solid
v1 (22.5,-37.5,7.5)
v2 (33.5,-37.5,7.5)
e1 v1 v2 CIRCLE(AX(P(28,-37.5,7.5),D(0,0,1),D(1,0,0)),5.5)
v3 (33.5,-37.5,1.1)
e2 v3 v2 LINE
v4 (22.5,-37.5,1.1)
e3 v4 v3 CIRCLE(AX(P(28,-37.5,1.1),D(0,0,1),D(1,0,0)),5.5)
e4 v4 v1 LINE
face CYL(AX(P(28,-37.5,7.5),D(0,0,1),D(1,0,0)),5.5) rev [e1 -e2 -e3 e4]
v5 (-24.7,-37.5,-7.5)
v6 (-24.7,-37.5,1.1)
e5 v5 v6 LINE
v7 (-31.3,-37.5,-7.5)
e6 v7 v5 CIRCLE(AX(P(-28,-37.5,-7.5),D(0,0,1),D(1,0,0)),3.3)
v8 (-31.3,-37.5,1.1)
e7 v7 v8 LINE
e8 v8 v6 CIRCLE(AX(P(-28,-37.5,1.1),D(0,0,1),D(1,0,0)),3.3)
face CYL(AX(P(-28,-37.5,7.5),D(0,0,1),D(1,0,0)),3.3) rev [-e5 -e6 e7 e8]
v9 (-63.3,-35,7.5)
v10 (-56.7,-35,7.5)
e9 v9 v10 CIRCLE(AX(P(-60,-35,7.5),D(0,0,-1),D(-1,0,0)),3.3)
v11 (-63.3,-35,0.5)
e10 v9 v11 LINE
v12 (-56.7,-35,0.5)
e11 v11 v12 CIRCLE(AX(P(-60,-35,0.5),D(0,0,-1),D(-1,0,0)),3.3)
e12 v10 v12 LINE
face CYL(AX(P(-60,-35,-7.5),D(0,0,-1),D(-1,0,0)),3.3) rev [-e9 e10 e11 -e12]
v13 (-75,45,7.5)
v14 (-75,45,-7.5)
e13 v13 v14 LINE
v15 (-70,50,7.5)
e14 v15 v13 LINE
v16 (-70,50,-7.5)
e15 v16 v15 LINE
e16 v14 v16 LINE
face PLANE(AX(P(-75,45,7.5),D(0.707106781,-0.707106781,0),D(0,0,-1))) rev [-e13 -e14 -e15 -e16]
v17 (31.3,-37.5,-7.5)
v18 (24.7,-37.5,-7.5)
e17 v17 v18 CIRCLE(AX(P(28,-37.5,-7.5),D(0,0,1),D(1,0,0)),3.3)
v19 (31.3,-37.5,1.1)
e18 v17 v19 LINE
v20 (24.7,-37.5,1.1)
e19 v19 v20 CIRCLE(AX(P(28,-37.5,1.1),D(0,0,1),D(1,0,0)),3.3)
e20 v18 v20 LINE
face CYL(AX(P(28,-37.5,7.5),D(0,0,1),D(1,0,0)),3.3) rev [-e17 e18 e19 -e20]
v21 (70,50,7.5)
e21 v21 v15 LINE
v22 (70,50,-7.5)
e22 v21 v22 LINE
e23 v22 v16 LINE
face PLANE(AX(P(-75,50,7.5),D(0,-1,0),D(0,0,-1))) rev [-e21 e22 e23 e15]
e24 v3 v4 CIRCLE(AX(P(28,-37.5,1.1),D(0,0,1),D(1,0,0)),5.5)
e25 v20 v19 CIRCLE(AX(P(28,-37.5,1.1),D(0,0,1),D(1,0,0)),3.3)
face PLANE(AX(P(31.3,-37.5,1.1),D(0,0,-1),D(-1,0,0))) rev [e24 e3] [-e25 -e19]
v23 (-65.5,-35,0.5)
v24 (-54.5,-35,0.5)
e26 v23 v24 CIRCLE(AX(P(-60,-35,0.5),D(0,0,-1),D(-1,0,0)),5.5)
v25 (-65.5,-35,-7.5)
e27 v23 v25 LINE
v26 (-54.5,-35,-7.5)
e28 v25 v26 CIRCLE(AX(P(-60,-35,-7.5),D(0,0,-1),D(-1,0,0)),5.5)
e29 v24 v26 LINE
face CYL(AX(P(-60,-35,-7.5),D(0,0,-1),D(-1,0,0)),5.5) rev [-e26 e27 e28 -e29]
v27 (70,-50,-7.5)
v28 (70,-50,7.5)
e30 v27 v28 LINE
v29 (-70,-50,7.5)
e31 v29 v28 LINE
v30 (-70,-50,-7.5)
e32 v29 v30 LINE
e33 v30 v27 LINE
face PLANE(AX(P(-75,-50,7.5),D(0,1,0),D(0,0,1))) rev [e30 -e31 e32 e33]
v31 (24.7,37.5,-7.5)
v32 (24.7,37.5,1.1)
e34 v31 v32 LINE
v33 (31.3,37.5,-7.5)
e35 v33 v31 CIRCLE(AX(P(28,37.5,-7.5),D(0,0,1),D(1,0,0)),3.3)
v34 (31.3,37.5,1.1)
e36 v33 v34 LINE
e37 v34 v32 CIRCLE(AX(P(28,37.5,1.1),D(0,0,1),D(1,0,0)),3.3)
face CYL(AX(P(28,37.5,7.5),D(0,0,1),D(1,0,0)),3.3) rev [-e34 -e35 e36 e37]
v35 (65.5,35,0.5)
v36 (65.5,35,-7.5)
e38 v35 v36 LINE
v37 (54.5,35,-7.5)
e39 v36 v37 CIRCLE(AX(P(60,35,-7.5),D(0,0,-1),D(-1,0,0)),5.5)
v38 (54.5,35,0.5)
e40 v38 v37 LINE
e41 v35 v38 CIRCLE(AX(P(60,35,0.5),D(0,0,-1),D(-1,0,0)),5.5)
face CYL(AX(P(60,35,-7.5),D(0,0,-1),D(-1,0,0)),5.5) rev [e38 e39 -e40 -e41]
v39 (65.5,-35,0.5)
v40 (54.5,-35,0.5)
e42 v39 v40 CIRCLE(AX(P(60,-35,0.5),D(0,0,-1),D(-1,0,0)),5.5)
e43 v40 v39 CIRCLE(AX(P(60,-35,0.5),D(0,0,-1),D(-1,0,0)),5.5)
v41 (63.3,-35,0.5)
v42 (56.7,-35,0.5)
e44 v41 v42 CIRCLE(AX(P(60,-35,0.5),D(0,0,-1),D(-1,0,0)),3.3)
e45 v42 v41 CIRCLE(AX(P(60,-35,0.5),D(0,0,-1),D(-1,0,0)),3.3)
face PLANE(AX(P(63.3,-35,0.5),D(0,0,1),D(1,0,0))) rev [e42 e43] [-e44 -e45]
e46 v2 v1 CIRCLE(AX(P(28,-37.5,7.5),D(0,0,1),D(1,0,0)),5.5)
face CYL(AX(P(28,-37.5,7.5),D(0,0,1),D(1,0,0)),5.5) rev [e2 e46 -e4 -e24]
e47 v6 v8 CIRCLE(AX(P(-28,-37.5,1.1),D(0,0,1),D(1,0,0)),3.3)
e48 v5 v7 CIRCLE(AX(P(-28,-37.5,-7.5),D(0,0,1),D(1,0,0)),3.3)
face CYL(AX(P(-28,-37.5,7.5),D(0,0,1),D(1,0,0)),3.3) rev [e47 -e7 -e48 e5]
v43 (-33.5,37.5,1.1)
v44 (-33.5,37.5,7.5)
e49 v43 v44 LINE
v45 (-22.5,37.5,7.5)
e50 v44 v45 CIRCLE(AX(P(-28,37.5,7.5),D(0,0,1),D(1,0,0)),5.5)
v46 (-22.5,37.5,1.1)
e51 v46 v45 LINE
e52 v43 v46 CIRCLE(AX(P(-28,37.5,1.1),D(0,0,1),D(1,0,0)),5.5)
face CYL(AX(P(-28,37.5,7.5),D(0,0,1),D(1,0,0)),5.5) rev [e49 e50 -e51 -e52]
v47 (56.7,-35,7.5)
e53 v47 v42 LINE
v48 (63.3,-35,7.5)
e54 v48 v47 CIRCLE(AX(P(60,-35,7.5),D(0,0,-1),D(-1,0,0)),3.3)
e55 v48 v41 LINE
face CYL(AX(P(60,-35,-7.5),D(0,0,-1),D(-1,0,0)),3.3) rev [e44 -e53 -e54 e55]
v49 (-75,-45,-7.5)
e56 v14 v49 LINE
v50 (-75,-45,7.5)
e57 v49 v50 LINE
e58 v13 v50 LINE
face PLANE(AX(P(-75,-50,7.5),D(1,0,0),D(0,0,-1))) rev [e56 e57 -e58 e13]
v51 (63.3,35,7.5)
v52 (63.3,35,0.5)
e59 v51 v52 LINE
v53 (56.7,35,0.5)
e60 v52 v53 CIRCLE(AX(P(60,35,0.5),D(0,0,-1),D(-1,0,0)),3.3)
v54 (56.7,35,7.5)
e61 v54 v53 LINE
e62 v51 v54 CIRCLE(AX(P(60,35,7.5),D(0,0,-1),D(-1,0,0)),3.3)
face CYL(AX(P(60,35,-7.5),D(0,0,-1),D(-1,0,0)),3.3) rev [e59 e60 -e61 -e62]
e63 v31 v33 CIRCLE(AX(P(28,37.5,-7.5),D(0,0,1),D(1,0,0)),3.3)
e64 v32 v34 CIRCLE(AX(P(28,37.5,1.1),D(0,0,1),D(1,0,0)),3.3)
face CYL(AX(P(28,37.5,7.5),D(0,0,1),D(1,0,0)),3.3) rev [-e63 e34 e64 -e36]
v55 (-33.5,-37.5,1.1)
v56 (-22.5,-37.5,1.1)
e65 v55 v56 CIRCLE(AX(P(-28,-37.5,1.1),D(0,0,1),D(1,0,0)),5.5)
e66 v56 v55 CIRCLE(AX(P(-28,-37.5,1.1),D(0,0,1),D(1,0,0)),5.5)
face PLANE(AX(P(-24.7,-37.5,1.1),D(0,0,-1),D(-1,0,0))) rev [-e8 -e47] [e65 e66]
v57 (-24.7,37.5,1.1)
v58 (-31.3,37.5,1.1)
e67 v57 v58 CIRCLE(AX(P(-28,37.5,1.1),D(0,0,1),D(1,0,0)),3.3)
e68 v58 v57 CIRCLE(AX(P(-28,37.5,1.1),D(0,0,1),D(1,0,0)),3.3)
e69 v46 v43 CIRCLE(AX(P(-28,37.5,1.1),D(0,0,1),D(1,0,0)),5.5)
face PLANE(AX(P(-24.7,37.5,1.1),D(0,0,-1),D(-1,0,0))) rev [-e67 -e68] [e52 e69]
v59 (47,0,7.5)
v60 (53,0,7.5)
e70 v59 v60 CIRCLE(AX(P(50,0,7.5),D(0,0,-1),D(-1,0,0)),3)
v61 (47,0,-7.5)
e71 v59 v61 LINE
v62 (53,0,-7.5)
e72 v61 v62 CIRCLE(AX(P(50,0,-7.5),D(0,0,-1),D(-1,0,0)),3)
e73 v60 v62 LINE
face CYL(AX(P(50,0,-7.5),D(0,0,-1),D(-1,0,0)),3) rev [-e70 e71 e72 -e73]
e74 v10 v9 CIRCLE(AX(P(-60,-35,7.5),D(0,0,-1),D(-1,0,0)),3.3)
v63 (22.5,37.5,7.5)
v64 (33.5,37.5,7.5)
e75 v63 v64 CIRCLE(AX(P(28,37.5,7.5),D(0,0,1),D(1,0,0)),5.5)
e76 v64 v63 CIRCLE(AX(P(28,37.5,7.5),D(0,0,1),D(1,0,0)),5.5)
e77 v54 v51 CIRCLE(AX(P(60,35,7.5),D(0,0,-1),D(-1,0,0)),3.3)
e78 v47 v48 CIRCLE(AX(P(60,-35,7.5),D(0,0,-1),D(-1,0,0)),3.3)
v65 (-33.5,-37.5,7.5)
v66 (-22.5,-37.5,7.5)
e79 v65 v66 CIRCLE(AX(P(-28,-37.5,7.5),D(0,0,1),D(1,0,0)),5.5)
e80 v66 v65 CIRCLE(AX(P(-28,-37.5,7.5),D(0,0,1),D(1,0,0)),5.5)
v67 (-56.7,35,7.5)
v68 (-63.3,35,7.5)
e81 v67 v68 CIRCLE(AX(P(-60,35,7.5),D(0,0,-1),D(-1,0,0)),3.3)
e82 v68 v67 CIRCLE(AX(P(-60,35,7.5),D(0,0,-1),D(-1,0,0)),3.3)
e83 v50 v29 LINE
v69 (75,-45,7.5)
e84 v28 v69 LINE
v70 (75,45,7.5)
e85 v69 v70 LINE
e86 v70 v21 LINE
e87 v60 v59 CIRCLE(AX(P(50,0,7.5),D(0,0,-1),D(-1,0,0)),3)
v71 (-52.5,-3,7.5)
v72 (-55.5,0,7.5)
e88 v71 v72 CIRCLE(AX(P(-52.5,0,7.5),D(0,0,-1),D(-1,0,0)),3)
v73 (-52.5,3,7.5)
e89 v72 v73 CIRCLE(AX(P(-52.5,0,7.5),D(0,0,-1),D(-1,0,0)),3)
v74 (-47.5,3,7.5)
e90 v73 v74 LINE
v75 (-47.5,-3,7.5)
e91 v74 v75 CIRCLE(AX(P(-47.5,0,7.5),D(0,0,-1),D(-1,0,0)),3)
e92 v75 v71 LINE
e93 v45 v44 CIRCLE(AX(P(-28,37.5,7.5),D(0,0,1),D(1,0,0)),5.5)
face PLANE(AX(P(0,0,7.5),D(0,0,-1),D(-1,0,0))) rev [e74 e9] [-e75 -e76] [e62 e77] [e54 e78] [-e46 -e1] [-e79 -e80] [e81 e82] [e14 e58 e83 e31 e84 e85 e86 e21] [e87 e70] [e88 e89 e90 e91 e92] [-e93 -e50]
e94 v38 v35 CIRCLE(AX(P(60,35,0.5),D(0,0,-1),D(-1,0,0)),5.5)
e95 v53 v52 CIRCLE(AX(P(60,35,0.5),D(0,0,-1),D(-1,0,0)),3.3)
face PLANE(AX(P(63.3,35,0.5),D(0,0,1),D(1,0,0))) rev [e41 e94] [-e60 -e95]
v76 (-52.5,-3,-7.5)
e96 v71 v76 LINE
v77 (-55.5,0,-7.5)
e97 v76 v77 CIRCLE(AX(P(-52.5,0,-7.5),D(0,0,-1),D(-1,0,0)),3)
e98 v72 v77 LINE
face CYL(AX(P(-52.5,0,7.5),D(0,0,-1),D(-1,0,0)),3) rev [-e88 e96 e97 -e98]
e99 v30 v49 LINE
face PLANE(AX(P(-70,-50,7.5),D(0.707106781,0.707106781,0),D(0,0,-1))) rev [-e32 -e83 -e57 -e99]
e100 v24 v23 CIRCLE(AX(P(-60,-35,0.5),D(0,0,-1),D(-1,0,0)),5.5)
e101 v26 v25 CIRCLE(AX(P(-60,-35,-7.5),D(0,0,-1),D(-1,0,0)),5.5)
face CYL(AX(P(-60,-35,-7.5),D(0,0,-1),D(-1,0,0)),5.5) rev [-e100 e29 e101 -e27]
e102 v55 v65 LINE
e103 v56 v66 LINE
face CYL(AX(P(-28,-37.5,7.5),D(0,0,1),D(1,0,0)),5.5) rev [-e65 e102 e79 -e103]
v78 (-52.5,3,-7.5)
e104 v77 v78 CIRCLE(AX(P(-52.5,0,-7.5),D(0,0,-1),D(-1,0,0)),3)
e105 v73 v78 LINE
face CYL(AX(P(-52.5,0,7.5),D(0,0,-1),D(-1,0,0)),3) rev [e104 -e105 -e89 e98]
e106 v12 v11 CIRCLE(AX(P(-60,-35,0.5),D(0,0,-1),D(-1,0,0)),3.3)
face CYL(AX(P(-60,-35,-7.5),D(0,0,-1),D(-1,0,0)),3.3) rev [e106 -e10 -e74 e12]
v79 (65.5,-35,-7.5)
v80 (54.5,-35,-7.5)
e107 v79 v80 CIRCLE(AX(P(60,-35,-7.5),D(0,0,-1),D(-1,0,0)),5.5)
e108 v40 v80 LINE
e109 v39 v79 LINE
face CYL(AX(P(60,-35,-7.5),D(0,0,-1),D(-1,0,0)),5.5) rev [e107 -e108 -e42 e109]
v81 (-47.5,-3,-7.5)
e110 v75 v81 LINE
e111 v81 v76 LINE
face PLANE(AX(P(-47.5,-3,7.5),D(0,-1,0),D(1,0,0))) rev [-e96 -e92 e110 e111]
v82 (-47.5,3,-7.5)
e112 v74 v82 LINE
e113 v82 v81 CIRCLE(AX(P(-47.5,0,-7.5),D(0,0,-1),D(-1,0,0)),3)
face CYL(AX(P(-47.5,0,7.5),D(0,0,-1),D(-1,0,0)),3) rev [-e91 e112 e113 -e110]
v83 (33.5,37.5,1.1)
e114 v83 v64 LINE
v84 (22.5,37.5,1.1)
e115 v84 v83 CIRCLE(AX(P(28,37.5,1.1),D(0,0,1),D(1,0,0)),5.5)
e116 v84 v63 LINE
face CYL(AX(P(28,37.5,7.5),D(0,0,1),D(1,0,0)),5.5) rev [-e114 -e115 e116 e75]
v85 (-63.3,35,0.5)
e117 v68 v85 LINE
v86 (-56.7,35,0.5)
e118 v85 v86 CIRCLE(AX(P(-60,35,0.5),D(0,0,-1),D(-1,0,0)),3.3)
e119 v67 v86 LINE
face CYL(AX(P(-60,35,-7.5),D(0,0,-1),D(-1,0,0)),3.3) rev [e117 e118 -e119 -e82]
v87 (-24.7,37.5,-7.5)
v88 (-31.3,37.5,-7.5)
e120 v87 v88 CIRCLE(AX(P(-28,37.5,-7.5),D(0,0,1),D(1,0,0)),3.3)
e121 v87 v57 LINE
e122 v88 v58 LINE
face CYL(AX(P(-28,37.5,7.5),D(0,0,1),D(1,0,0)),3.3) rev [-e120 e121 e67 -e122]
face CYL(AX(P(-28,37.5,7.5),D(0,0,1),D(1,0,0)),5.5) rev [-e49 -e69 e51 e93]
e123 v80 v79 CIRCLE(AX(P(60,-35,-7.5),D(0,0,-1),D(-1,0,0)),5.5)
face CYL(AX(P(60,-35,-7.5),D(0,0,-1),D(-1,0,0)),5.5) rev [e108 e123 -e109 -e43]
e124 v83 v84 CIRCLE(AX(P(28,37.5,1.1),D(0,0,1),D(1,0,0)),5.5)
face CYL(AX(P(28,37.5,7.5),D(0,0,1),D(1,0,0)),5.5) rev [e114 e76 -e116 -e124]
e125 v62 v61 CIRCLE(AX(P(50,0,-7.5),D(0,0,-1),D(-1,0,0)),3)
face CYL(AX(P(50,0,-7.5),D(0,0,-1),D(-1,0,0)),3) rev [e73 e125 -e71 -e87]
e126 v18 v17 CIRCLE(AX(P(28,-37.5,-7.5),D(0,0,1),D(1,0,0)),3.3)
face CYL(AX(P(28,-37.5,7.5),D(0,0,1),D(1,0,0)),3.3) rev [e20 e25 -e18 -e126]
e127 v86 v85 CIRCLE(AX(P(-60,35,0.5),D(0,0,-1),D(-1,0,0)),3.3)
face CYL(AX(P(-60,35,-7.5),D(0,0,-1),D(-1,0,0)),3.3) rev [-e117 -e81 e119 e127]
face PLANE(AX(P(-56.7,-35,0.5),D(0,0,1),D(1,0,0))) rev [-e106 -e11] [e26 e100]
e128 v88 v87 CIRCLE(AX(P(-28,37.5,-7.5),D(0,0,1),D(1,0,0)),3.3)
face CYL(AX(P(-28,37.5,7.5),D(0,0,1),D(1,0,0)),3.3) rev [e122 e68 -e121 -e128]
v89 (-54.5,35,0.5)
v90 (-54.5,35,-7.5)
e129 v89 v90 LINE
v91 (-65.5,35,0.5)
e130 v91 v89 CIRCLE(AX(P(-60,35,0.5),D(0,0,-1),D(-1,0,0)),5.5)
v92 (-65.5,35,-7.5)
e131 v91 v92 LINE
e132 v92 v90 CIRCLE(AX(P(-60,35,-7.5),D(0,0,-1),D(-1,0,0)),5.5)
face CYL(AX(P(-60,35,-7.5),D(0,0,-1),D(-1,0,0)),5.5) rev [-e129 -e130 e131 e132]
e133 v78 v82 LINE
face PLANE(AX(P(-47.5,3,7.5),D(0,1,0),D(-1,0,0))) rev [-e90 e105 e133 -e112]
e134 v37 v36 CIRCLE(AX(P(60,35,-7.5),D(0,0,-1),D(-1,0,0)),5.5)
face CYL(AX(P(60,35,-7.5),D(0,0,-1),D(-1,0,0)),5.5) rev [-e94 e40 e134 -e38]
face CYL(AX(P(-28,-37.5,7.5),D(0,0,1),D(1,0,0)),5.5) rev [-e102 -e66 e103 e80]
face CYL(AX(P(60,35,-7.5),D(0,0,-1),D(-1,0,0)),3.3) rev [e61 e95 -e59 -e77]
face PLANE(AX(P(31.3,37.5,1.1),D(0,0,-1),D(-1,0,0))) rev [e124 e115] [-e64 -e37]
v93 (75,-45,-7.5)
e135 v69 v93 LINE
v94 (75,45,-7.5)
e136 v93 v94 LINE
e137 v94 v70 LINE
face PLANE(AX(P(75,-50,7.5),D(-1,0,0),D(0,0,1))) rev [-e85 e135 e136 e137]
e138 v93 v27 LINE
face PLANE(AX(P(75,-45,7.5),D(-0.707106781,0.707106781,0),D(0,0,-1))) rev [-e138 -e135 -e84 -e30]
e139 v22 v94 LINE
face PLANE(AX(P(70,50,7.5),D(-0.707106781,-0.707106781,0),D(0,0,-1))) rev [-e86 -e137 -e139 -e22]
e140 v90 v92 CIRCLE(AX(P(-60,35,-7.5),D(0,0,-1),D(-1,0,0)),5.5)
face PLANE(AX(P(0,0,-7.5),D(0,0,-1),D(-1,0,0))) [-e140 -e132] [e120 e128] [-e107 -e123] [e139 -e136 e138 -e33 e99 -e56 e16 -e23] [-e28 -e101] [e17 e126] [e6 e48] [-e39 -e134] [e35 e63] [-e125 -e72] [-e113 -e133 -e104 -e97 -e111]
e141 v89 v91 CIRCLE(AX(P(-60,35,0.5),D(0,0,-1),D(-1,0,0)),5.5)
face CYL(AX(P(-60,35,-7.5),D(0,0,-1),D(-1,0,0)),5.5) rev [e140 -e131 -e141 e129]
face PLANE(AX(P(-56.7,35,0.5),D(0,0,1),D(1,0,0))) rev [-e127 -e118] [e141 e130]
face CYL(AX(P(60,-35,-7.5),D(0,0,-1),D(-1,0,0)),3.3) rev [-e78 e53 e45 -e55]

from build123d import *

# Parameters (mm, degrees)
SKETCH_1_W                   = 150
SKETCH_1_H                   = 100
EXTRUDE_1_DEPTH              = 7.5
HOLE_WIZARD_M6_1_D           = 6.6
HOLE_WIZARD_M6_1_CBORE_D     = 11
HOLE_WIZARD_M6_1_CBORE_DEPTH = 6.4
CHAMFER_1_SIZE               = 5
HOLE_WIZARD_M6_2_D           = 6.6
HOLE_WIZARD_M6_2_CBORE_D     = 11
HOLE_WIZARD_M6_2_CBORE_DEPTH = 8
MM_1_D                       = 6
CUT_EXTRUDE_1_DEPTH          = 92.378334412


with BuildPart() as part:
    # 草图1 → 凸台-拉伸1 (new, symmetric)
    with BuildSketch(Plane.XY):
        Rectangle(SKETCH_1_W, SKETCH_1_H)
    extrude(amount=EXTRUDE_1_DEPTH, both=True)

    # M6 六角凹头螺钉的柱形沉头孔1 (through all)
    with Locations(Plane.XY.offset(7.5)):
        with Locations((-28, -37.5), (-28, 37.5), (28, 37.5), (28, -37.5)):
            CounterBoreHole(HOLE_WIZARD_M6_1_D / 2, HOLE_WIZARD_M6_1_CBORE_D / 2, HOLE_WIZARD_M6_1_CBORE_DEPTH)

    # 倒角1
    chamfer_1_edges = [part.edges().sort_by_distance(p)[0] for p in [
        (75, -50, 0),
        (-75, -50, 0),
        (-75, 50, 0),
        (75, 50, 0),
    ]]
    chamfer(chamfer_1_edges, length=CHAMFER_1_SIZE)

    # M6 六角凹头螺钉的柱形沉头孔2 (through all)
    with Locations(Plane(origin=(0, 0, -7.5), x_dir=(-1, 0, 0), z_dir=(0, 0, -1))):
        with Locations((-60, -35), (-60, 35), (60, 35), (60, -35)):
            CounterBoreHole(HOLE_WIZARD_M6_2_D / 2, HOLE_WIZARD_M6_2_CBORE_D / 2, HOLE_WIZARD_M6_2_CBORE_DEPTH)

    # 大小mm 暗销孔1 (through all)
    with Locations(Plane(origin=(0, 0, -7.5), x_dir=(-1, 0, 0), z_dir=(0, 0, -1))):
        with Locations((50, 0), (-50, 0)):
            Hole(MM_1_D / 2)

    # 草图8 → 切除-拉伸1 (cut, through all)
    with BuildSketch(Plane(origin=(0, 0, -7.5), x_dir=(-1, 0, 0), z_dir=(0, 0, -1))):
        with BuildLine():
            Line((47.5, 3), (52.5, 3))
            ThreePointArc((52.5, 3), (55.5, 0), (52.5, -3))
            Line((52.5, -3), (47.5, -3))
            ThreePointArc((47.5, -3), (44.5, 0), (47.5, 3))
        make_face()
    extrude(amount=-CUT_EXTRUDE_1_DEPTH, mode=Mode.SUBTRACT)


solid = part.part
